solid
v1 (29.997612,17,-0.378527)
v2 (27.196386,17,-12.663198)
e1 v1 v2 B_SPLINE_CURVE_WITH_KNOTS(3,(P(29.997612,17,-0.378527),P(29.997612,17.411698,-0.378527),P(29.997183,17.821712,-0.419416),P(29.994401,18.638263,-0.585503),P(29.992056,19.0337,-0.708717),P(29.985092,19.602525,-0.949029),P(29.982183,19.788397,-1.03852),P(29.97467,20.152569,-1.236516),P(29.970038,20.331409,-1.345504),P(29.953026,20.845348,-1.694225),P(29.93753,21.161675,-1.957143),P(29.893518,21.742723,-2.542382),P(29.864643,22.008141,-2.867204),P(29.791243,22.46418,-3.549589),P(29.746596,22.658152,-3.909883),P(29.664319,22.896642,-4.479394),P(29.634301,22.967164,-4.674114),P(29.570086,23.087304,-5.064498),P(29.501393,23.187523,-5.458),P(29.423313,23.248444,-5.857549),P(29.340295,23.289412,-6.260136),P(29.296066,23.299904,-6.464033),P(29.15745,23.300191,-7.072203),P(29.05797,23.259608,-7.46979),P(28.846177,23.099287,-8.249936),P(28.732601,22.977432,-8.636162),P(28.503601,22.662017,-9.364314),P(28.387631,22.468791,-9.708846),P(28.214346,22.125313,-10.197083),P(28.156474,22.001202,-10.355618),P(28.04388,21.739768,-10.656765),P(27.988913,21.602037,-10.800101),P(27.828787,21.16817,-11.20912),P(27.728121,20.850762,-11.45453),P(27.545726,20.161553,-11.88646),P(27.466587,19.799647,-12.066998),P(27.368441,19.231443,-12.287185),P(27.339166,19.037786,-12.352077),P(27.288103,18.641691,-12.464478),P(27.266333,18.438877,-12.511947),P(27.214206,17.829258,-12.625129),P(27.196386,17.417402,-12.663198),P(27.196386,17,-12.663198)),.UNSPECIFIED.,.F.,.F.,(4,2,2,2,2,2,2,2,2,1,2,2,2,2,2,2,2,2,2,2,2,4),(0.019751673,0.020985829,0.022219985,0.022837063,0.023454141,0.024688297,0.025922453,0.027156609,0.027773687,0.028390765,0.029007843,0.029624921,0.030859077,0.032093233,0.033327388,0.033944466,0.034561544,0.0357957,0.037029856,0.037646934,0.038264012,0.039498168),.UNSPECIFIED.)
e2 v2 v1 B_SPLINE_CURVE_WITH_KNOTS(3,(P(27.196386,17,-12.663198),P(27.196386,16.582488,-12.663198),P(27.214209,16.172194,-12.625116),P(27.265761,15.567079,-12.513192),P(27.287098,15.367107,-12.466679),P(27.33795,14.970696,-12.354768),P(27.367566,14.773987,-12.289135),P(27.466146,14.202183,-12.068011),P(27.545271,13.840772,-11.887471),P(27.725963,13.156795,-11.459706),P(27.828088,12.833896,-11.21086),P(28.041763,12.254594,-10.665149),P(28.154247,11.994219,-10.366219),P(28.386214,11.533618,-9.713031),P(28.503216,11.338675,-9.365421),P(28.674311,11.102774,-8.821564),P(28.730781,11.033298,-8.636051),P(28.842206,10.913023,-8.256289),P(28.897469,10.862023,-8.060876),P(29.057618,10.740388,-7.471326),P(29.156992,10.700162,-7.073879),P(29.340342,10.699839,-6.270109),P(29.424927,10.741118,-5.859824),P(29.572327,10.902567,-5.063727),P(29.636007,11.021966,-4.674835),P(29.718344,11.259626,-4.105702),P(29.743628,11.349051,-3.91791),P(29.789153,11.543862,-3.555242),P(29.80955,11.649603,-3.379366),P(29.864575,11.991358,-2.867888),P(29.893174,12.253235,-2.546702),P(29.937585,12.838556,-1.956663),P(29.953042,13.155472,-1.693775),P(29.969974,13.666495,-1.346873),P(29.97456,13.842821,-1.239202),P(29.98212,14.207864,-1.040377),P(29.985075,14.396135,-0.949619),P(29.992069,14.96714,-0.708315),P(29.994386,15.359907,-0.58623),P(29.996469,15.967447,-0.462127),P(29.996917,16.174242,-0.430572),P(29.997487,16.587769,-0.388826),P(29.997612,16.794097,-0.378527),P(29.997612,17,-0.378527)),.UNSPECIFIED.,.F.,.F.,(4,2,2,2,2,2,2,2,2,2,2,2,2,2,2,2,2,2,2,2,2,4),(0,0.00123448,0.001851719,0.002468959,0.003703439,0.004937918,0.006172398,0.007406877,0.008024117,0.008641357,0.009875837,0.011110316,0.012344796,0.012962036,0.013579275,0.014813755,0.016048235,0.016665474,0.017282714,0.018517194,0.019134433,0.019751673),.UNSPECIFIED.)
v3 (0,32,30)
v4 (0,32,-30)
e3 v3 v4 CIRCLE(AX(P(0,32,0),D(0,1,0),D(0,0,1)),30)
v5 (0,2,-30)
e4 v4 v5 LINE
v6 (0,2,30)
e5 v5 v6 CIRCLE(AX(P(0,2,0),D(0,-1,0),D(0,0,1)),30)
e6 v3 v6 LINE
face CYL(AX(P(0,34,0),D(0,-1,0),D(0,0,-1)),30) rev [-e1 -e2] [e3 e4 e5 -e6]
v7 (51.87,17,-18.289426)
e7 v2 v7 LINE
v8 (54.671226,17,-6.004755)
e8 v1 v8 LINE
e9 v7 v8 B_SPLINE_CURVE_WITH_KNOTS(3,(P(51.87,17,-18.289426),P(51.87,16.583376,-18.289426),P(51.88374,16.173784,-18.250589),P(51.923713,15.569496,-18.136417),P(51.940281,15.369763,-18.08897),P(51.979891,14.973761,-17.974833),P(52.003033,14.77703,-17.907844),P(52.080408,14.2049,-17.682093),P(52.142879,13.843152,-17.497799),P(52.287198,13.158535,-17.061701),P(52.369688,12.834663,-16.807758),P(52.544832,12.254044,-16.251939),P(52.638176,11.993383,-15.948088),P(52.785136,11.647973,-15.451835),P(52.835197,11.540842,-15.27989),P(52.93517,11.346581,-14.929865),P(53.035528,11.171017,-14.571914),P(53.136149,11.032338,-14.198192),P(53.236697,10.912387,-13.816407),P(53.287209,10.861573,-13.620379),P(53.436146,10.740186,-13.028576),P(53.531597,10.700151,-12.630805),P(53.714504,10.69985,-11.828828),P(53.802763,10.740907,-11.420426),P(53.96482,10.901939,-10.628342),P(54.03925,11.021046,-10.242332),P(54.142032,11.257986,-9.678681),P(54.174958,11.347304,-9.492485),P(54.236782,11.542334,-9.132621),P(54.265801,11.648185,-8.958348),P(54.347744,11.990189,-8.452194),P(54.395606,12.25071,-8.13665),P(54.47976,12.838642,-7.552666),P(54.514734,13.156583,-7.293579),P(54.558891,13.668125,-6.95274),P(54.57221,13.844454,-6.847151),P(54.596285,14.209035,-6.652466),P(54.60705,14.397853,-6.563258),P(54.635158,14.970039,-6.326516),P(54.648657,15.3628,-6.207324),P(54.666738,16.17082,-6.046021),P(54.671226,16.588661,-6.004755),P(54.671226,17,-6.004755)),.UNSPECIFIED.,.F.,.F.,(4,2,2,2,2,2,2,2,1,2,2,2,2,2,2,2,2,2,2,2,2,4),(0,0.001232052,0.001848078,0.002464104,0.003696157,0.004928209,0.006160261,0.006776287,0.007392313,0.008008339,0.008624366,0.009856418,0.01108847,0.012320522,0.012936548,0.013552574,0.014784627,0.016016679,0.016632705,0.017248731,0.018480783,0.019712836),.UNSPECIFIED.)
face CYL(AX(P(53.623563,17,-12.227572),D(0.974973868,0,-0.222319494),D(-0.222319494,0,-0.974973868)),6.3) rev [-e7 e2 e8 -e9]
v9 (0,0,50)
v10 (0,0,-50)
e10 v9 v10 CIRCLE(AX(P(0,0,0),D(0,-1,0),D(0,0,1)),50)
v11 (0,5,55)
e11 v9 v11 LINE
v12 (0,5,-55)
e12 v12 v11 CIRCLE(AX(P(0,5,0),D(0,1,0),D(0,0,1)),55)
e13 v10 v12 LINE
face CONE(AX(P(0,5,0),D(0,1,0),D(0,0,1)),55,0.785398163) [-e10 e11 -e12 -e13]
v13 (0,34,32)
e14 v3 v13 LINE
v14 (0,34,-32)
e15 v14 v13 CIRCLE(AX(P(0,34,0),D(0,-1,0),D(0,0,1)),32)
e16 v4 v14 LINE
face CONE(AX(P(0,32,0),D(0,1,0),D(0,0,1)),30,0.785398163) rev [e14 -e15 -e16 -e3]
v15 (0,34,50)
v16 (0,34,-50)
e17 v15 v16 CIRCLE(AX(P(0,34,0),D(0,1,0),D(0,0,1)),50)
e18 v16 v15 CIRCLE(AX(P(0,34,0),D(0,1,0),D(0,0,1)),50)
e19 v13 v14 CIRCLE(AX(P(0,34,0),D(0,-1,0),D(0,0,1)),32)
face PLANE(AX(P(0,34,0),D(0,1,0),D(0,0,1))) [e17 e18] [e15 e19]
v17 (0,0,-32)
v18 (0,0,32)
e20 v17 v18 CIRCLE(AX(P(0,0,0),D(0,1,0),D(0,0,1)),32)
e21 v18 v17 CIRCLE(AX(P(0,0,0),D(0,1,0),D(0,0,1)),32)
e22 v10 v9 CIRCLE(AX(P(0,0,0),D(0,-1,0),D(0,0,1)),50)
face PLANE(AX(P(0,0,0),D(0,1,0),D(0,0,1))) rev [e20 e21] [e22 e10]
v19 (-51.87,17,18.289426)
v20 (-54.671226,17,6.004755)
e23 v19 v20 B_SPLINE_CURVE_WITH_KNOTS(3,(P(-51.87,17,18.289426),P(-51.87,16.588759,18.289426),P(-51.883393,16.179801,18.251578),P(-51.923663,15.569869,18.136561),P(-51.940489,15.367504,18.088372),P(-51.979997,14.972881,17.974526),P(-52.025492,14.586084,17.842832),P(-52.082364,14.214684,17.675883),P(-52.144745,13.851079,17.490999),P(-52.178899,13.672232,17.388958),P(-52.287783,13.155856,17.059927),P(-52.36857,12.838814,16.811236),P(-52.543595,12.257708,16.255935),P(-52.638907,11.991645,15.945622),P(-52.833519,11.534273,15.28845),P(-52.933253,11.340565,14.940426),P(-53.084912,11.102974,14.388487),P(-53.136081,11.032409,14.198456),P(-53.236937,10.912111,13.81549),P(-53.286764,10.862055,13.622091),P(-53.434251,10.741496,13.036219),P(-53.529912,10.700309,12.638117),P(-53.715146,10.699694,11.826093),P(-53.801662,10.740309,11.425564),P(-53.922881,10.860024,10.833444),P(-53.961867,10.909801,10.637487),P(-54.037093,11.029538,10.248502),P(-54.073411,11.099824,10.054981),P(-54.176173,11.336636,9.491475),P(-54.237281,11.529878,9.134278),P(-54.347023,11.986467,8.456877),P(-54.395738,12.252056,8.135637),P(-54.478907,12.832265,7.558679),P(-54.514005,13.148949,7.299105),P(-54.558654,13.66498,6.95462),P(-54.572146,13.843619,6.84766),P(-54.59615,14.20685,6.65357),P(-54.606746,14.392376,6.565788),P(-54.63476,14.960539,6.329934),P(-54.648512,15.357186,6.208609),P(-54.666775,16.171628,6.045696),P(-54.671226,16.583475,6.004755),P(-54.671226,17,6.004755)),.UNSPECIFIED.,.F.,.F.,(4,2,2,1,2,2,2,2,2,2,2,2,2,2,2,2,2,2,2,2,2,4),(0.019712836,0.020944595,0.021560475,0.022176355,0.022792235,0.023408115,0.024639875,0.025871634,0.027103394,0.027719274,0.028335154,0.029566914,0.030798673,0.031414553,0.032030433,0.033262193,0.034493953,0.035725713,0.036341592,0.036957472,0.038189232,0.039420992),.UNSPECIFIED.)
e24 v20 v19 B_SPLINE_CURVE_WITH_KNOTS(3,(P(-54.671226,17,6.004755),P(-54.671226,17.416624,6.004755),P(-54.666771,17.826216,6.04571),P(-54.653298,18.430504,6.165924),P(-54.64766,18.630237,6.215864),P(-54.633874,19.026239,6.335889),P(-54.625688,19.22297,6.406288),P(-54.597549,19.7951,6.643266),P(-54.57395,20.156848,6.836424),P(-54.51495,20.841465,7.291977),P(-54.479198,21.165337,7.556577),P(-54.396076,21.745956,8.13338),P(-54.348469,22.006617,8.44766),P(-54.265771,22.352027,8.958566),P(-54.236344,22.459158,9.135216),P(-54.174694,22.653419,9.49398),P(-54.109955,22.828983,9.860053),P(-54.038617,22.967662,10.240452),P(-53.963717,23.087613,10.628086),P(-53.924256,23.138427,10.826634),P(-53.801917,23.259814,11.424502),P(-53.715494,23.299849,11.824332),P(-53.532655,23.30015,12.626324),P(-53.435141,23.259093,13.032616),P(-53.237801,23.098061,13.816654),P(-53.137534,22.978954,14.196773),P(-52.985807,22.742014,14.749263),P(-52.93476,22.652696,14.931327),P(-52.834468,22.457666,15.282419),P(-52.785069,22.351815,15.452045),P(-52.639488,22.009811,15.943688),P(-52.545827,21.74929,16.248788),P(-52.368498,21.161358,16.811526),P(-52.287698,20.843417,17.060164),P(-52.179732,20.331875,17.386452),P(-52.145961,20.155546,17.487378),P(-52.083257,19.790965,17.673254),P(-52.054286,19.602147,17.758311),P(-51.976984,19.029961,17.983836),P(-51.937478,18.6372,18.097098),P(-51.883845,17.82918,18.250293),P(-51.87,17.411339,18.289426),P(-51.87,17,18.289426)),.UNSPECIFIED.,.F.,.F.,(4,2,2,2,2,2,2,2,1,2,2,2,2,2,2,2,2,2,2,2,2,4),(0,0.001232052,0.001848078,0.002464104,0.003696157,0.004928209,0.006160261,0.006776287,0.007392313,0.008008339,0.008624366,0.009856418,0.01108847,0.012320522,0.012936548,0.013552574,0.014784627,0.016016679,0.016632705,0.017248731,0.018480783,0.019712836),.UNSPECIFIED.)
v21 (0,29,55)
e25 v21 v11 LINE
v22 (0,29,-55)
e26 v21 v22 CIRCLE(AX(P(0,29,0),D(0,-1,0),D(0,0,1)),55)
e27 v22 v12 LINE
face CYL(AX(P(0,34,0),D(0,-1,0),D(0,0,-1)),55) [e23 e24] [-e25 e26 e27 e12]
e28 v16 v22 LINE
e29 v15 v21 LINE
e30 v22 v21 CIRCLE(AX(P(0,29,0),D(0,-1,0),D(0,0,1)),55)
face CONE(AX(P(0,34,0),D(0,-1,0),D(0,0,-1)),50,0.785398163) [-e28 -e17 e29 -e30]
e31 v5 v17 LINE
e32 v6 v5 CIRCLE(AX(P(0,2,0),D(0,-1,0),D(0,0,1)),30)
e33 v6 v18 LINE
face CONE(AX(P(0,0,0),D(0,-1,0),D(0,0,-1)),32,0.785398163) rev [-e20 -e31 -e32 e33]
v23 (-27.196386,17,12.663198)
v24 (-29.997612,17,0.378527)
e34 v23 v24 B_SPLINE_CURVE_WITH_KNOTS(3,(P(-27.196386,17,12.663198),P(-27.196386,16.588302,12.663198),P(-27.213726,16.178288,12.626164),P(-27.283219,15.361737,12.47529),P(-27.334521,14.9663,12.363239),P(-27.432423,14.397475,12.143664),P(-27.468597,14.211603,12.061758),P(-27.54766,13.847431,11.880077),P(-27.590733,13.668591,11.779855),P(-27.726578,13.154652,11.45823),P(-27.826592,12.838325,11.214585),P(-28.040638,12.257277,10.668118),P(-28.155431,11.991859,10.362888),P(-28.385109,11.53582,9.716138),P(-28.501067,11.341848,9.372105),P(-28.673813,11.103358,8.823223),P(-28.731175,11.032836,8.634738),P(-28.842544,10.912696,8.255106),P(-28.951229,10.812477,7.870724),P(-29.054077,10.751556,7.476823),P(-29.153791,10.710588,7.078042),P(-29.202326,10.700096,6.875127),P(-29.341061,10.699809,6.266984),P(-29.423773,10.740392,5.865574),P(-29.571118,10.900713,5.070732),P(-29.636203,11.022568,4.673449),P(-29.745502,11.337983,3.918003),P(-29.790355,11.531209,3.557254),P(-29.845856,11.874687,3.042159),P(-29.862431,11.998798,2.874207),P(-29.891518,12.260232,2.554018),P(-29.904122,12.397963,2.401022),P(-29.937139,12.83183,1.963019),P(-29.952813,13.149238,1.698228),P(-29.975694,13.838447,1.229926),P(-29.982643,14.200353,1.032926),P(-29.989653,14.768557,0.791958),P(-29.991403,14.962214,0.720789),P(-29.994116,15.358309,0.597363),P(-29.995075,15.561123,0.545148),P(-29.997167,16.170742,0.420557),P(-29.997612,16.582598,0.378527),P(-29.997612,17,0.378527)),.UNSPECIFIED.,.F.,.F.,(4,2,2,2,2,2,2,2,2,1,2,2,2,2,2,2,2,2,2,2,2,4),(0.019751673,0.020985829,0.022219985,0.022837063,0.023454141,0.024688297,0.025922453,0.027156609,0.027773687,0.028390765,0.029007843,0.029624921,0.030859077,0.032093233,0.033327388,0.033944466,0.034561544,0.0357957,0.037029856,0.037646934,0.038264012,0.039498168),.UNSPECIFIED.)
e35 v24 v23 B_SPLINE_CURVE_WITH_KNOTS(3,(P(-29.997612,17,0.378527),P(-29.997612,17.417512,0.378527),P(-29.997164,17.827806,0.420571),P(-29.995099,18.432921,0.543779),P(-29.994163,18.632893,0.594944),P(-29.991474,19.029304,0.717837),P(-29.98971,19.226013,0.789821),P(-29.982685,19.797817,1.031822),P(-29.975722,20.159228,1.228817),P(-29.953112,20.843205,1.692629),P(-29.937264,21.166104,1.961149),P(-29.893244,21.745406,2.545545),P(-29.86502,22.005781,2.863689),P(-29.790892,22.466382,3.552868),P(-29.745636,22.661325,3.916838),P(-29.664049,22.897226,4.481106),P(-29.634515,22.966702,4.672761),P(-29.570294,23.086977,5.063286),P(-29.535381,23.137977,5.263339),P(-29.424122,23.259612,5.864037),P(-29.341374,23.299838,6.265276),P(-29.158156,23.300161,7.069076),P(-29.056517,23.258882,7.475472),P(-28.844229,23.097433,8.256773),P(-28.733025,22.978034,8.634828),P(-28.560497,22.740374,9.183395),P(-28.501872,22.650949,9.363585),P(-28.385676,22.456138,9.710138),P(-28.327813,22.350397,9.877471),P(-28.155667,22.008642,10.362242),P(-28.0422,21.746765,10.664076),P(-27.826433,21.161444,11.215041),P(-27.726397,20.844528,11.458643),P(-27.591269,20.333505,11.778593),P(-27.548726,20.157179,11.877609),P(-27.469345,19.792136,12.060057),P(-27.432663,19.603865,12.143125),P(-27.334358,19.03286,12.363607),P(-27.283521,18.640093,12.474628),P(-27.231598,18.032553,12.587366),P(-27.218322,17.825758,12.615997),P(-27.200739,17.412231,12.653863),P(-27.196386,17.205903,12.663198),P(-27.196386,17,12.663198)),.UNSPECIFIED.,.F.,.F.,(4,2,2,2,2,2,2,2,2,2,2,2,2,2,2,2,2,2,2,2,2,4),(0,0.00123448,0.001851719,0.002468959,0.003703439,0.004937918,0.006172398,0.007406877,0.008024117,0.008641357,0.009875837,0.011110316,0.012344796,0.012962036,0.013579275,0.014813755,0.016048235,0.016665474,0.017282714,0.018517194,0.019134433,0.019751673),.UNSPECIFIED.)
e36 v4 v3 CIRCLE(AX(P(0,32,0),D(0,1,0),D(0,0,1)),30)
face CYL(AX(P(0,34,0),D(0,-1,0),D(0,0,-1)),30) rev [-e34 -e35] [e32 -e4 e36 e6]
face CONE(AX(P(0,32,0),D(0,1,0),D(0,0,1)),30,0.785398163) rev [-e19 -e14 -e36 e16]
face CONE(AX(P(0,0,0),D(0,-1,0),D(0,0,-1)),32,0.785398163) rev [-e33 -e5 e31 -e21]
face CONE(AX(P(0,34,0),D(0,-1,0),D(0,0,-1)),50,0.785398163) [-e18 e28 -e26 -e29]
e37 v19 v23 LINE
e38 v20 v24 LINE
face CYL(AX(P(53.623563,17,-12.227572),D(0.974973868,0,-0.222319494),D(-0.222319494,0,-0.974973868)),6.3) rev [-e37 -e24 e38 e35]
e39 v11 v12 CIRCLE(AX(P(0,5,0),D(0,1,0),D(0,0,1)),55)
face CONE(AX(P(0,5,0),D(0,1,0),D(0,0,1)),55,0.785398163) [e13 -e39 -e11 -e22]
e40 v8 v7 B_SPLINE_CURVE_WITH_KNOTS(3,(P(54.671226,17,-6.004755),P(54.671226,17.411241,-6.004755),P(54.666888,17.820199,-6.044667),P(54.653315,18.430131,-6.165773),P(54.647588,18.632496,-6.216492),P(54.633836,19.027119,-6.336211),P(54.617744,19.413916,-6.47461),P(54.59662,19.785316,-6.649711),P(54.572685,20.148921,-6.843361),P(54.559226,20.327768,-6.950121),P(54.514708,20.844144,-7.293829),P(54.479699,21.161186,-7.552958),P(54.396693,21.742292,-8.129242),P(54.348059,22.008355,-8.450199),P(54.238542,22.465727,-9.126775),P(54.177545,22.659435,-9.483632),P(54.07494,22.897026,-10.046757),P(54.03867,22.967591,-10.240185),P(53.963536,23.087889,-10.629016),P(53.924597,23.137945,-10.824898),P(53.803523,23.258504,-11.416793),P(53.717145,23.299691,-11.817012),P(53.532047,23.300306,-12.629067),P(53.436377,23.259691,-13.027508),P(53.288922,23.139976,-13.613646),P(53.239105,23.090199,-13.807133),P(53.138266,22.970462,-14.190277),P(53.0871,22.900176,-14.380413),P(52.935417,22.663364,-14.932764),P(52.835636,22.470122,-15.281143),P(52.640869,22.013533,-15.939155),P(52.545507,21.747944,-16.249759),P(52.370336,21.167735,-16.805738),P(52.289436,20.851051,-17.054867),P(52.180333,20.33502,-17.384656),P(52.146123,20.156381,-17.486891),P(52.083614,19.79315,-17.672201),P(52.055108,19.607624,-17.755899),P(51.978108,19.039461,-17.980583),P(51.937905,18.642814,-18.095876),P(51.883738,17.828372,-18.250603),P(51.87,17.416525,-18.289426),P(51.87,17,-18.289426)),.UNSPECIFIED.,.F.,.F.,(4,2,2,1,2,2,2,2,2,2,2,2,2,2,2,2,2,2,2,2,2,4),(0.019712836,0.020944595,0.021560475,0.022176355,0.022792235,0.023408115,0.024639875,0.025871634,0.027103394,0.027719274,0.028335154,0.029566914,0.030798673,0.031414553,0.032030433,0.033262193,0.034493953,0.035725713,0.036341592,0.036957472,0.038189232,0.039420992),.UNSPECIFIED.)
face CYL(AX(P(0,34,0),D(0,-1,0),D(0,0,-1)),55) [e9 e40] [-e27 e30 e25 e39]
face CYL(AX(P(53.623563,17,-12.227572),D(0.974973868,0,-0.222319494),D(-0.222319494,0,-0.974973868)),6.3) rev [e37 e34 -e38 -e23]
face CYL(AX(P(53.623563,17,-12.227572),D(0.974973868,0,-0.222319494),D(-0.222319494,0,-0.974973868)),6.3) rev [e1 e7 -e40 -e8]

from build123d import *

# Parameters (mm, degrees)
SKETCH1_R                  = 55
SKETCH1_R_2                = 30
BOSS_EXTRUDE1_DEPTH        = 34
F_17_0_17_DIAMETER_HOLE1_D = 12.6
CHAMFER1_SIZE              = 5
CHAMFER2_SIZE              = 2


with BuildPart() as part:
    # Sketch1 → Boss-Extrude1 (new body)
    with BuildSketch(Plane(origin=(0, 0, 0), x_dir=(1, 0, 0), z_dir=(0, 1, 0))):
        with Locations(Location((0, 0, 0), (0, 0, 270))):
            Circle(SKETCH1_R)
        with Locations(Location((0, 0, 0), (0, 0, 270))):
            Circle(SKETCH1_R_2, mode=Mode.SUBTRACT)
    extrude(amount=BOSS_EXTRUDE1_DEPTH)

    # Ø17.0 (17) Diameter Hole1 (through all)
    with Locations(Plane(origin=(53.62356272, 17, -12.227572173), x_dir=(0.22231949406, 0, 0.97497386763), z_dir=(0.97497386763, 0, -0.22231949406))):
        with Locations((0, 0)):
            Hole(F_17_0_17_DIAMETER_HOLE1_D / 2)

    # Chamfer1
    chamfer1_edges = [part.edges().sort_by_distance(p)[0] for p in [
        (0, 0, -55),
        (0, 34, -55),
    ]]
    chamfer(chamfer1_edges, length=CHAMFER1_SIZE)

    # Chamfer2
    chamfer2_edges = [part.edges().sort_by_distance(p)[0] for p in [
        (0, 0, -30),
        (0, 34, -30),
    ]]
    chamfer(chamfer2_edges, length=CHAMFER2_SIZE)


solid = part.part
